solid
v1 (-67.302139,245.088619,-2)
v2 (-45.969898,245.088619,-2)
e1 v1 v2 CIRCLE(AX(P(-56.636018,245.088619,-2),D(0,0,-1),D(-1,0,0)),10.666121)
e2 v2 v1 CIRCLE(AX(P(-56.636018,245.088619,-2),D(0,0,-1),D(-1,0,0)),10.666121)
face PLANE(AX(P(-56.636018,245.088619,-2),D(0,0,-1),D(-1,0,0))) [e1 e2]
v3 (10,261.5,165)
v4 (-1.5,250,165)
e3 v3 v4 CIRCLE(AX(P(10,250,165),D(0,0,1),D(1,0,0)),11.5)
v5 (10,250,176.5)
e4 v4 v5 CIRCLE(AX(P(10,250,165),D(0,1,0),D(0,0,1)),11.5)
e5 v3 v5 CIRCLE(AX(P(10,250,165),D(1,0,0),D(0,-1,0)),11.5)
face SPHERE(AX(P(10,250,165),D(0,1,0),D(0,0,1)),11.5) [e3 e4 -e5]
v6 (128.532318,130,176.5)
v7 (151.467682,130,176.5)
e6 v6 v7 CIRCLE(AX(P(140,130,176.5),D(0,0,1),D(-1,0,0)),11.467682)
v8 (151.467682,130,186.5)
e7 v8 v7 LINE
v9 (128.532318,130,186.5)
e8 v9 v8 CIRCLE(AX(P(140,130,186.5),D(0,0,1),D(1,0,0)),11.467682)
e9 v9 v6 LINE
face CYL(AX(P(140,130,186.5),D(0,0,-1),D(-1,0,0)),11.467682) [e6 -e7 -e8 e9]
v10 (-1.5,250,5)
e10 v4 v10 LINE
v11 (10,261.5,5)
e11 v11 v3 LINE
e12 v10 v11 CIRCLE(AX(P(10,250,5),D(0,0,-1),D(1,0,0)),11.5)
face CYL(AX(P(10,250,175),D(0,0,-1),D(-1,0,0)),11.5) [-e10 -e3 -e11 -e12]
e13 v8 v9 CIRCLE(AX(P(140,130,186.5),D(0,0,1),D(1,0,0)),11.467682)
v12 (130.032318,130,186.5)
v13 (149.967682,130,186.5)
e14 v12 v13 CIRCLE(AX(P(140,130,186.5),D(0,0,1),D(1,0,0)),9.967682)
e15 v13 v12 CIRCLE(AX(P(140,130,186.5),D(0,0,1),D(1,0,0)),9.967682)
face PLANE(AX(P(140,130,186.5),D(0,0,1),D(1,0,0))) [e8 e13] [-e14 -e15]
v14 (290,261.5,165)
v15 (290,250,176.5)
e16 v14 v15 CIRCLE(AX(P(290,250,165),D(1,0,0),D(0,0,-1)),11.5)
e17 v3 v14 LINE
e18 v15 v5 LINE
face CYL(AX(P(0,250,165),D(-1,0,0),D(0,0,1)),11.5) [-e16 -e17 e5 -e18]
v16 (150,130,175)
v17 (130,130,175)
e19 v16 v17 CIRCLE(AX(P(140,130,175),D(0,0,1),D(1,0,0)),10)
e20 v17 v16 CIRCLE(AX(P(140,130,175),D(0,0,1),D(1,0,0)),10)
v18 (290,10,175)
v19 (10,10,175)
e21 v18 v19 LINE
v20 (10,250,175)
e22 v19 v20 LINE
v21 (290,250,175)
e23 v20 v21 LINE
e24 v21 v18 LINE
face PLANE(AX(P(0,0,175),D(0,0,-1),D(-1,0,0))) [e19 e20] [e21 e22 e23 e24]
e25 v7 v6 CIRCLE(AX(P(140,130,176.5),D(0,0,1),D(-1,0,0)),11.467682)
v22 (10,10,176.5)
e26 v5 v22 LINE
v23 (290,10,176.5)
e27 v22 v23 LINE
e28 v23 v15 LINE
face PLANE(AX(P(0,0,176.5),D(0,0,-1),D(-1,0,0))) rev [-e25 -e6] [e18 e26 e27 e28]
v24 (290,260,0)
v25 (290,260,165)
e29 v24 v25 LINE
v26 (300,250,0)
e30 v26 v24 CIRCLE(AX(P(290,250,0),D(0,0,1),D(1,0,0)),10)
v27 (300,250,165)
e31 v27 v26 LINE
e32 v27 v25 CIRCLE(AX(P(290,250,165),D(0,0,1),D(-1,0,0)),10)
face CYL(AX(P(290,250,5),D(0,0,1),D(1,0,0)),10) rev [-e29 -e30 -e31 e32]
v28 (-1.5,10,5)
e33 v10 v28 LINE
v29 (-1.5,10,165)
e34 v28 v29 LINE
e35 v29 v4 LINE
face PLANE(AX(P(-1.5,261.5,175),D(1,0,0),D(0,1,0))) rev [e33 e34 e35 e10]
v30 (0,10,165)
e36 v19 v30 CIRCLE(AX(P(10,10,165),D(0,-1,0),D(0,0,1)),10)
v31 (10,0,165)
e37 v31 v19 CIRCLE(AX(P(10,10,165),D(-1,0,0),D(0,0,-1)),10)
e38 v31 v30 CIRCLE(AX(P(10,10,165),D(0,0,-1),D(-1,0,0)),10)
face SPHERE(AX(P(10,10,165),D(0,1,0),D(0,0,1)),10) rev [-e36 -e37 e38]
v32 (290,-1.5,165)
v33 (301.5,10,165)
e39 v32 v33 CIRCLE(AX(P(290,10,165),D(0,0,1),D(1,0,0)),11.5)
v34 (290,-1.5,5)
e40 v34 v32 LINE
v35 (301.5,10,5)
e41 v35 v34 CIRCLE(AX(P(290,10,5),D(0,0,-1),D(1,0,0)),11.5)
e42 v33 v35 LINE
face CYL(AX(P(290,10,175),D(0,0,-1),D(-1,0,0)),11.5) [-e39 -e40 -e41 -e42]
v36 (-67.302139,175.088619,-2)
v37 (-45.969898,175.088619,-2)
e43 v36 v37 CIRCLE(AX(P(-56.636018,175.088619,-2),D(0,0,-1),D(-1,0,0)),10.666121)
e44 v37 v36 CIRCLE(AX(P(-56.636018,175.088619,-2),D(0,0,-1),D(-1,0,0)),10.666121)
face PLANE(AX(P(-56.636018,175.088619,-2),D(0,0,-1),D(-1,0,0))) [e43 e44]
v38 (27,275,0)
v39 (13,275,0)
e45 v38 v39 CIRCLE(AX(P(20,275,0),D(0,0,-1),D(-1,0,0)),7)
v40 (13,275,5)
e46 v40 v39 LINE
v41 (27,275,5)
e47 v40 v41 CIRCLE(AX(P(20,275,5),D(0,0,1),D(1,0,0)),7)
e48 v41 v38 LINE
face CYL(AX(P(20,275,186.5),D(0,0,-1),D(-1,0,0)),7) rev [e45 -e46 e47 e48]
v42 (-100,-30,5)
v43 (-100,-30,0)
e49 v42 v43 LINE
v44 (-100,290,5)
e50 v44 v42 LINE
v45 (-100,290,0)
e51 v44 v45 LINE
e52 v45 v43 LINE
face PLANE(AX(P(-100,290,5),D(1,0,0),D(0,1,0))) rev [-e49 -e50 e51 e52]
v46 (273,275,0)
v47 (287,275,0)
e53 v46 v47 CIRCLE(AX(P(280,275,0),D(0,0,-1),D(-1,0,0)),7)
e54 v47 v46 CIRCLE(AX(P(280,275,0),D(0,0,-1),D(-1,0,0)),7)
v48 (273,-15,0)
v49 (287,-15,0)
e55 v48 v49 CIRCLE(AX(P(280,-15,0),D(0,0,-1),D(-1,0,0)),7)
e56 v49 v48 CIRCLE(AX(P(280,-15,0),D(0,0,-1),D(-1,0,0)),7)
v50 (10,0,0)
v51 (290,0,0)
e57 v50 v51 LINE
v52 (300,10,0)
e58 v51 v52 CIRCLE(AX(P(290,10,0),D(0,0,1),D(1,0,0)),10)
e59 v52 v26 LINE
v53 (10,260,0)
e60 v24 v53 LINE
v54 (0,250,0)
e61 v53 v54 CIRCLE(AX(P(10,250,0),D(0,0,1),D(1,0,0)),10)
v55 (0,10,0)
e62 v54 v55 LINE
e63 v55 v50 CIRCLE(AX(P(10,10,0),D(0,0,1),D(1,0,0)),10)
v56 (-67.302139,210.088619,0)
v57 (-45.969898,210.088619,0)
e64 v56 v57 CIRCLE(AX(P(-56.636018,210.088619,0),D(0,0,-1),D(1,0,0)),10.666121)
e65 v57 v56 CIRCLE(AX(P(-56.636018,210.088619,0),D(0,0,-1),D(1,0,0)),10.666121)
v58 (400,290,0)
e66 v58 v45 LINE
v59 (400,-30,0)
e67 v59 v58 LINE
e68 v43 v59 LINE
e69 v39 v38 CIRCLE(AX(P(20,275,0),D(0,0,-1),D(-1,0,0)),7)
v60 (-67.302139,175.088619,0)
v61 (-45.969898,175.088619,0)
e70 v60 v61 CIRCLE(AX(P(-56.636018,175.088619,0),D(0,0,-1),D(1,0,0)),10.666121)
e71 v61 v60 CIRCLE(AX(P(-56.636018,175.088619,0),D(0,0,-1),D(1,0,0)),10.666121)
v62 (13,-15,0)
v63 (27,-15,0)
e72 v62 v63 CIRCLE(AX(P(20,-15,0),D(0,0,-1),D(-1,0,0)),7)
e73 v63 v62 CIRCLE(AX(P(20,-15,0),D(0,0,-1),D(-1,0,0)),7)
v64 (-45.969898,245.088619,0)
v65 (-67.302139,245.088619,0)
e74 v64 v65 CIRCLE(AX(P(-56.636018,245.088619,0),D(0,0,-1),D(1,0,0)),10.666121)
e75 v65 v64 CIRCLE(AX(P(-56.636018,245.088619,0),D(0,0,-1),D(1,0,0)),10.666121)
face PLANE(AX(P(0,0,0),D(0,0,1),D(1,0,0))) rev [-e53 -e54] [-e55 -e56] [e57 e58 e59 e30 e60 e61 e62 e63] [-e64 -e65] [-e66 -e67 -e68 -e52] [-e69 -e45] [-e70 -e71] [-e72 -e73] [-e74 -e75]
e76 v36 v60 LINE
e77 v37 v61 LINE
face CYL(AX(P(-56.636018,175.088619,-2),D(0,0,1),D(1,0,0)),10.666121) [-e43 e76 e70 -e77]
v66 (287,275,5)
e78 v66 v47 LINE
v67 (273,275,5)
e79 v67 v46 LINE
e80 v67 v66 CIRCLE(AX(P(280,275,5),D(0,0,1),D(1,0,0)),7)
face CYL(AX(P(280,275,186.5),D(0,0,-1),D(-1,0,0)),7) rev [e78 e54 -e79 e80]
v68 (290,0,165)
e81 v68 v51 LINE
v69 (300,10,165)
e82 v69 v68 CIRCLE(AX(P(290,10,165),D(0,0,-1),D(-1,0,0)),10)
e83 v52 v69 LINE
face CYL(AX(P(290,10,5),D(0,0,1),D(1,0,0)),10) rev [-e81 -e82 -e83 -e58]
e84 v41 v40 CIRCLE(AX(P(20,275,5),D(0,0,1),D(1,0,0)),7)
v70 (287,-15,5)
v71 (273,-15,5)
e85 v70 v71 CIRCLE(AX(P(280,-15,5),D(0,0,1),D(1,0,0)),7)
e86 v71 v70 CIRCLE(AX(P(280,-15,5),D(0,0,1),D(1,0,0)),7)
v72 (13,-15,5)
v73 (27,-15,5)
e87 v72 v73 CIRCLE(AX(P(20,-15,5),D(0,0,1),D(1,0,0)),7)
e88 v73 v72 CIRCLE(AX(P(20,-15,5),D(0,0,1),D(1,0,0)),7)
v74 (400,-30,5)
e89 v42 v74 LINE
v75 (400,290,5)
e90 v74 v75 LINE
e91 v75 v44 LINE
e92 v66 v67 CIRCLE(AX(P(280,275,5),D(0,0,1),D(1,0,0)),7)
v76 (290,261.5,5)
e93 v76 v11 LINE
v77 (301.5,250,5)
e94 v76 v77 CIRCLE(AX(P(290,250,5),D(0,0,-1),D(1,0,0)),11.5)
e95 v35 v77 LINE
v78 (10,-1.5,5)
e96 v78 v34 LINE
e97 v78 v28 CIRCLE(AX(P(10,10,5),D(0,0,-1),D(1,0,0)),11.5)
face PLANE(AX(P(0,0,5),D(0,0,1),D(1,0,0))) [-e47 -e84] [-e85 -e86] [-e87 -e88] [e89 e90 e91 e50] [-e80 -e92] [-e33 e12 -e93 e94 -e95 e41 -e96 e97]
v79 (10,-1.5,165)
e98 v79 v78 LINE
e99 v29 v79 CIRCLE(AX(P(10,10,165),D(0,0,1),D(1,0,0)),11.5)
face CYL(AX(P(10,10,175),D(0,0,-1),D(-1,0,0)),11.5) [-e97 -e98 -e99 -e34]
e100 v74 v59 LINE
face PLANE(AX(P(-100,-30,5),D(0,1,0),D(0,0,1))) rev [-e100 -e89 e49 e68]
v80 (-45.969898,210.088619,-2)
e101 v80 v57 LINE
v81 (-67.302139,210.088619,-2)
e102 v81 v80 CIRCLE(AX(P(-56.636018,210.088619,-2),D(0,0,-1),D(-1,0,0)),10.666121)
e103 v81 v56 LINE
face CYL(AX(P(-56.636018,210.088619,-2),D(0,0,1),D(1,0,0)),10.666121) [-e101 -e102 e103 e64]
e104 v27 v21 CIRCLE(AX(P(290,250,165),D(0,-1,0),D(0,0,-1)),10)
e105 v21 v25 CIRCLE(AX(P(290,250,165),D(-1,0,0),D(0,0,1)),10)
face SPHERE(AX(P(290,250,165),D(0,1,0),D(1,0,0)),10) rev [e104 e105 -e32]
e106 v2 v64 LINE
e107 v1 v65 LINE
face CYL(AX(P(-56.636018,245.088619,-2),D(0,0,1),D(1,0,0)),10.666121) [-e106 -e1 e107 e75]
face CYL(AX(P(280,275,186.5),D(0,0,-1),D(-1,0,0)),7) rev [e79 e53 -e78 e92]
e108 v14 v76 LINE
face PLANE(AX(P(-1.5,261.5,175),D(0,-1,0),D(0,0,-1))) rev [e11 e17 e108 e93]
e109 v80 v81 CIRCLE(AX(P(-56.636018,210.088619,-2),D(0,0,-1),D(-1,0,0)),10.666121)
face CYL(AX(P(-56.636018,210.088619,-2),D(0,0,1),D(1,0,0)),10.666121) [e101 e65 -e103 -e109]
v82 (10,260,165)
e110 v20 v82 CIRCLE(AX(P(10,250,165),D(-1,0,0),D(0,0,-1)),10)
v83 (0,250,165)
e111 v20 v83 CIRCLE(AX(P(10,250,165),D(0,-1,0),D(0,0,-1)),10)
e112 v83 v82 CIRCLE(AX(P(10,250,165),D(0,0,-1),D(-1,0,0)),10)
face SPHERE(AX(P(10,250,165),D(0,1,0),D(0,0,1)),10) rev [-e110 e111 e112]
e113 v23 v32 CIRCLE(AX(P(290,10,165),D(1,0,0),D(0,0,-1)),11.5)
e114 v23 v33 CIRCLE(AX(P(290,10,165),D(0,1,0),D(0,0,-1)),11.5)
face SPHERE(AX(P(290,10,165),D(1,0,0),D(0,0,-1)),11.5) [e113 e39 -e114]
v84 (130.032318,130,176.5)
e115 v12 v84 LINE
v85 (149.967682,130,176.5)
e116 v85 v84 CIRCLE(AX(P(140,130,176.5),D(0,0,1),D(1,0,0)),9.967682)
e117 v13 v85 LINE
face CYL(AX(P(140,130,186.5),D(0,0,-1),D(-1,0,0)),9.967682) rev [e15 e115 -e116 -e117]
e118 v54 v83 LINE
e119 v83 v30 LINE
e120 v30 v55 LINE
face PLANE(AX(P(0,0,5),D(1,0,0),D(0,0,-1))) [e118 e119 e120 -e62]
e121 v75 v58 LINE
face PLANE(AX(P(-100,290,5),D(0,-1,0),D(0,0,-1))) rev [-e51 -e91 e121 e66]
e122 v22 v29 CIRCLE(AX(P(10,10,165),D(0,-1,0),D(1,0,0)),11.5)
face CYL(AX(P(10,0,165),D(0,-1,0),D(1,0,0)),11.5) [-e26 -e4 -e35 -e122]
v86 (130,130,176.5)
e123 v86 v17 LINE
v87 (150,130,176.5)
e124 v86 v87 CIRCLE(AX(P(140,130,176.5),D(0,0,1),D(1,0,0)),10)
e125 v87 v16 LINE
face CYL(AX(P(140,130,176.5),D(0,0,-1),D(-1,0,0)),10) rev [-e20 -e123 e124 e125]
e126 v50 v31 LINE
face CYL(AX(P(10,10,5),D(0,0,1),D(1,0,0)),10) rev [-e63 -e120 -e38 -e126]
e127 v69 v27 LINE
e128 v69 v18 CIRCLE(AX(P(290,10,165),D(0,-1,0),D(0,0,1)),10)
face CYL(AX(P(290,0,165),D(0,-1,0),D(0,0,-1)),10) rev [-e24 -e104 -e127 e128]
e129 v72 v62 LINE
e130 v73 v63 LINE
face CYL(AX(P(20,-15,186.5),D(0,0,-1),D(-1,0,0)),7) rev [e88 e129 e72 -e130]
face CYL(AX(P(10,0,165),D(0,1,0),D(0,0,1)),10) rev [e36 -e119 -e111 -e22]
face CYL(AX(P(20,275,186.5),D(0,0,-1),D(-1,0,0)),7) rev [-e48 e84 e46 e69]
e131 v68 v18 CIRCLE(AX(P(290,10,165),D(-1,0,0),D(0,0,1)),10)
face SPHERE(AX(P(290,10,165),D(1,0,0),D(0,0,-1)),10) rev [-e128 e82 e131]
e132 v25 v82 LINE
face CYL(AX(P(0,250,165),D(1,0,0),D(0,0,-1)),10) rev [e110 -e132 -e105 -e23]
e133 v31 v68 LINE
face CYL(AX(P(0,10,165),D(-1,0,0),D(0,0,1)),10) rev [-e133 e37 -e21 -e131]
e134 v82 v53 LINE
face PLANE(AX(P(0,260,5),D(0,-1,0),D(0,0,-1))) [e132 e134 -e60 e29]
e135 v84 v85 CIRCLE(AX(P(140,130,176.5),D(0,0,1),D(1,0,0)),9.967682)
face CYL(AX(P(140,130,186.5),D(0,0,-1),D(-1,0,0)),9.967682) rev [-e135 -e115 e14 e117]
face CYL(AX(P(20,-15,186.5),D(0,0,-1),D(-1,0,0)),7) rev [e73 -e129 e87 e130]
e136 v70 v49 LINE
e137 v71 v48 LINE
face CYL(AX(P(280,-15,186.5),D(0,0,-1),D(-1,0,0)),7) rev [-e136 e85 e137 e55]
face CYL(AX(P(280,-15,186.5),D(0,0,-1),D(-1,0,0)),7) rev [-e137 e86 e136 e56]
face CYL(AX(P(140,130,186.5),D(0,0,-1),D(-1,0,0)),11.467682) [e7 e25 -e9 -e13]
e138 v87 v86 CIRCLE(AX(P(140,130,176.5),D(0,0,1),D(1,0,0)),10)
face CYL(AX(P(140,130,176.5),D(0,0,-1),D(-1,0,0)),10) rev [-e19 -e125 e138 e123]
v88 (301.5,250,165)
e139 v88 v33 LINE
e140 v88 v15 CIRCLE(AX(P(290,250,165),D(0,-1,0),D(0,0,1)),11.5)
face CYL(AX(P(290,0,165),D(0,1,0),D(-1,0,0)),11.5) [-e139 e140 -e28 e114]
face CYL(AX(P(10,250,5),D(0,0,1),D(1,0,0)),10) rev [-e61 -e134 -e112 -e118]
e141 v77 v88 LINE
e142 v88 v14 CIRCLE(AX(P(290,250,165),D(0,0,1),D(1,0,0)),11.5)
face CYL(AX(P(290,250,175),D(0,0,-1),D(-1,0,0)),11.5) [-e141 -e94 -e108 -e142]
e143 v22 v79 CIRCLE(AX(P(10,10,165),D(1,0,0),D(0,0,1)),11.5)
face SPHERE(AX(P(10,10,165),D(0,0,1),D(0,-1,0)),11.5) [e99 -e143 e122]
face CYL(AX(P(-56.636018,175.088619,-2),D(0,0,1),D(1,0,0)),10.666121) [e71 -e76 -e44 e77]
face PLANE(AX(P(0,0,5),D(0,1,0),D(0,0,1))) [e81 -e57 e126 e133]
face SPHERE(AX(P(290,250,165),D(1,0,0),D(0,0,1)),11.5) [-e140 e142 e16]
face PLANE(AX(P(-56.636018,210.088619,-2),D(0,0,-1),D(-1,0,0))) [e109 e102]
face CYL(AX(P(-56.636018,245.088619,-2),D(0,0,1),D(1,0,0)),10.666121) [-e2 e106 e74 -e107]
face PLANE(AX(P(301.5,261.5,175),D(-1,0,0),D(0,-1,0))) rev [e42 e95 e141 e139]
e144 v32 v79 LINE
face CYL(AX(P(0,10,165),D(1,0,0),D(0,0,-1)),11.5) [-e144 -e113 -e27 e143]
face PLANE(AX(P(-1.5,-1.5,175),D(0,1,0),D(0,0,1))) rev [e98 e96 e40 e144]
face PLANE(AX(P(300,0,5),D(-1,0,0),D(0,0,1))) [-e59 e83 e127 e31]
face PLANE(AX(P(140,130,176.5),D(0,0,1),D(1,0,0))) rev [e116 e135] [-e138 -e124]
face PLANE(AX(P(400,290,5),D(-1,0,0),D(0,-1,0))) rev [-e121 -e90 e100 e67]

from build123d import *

# Parameters (mm, degrees)
SKETCH1_W           = 500
SKETCH1_H           = 320
SKETCH1_W_2         = 300
SKETCH1_H_2         = 260
BOSS_EXTRUDE1_DEPTH = 5
SKETCH2_W           = 303
SKETCH2_H           = 263
SKETCH2_W_2         = 300
SKETCH2_H_2         = 260
BOSS_EXTRUDE2_DEPTH = 170
SKETCH3_W           = 303
SKETCH3_H           = 263
SKETCH3_R           = 10
BOSS_EXTRUDE3_DEPTH = 1.5
FILLET2_R           = 10
FILLET3_R           = 11.5
SKETCH4_R           = 11.467682252
SKETCH4_R_2         = 9.967682252
BOSS_EXTRUDE4_DEPTH = 10
SKETCH5_R           = 7
CUT_EXTRUDE1_DEPTH  = 529.093031577
SKETCH6_R           = 10.66612067
BOSS_EXTRUDE5_DEPTH = 2


with BuildPart() as part:
    # Sketch1 → Boss-Extrude1 (new body)
    with BuildSketch(Plane.XY):
        with Locations((150, 130)):
            Rectangle(SKETCH1_W, SKETCH1_H)
        with Locations((150, 130)):
            Rectangle(SKETCH1_W_2, SKETCH1_H_2, mode=Mode.SUBTRACT)
    extrude(amount=BOSS_EXTRUDE1_DEPTH)

    # Sketch2 → Boss-Extrude2 (add)
    with BuildSketch(Plane.XY.offset(5)):
        with Locations((150, 130)):
            Rectangle(SKETCH2_W, SKETCH2_H)
        with Locations((150, 130)):
            Rectangle(SKETCH2_W_2, SKETCH2_H_2, mode=Mode.SUBTRACT)
    extrude(amount=BOSS_EXTRUDE2_DEPTH)

    # Sketch3 → Boss-Extrude3 (add)
    with BuildSketch(Plane.XY.offset(175)):
        with Locations((150, 130)):
            Rectangle(SKETCH3_W, SKETCH3_H)
        with Locations((140, 130)):
            Circle(SKETCH3_R, mode=Mode.SUBTRACT)
    extrude(amount=BOSS_EXTRUDE3_DEPTH)

    # Fillet2
    fillet2_edges = [part.edges().sort_by_distance(p)[0] for p in [
        (0, 260, 87.5),
        (0, 0, 87.5),
        (300, 0, 87.5),
        (300, 260, 87.5),
        (0, 130, 175),
        (150, 0, 175),
        (300, 130, 175),
        (150, 260, 175),
    ]]
    fillet(fillet2_edges, radius=FILLET2_R)

    # Fillet3
    fillet3_edges = [part.edges().sort_by_distance(p)[0] for p in [
        (-1.5, 261.5, 90.75),
        (-1.5, -1.5, 90.75),
        (301.5, -1.5, 90.75),
        (301.5, 261.5, 90.75),
        (301.5, 130, 176.5),
        (150, 261.5, 176.5),
        (-1.5, 130, 176.5),
        (150, -1.5, 176.5),
    ]]
    fillet(fillet3_edges, radius=FILLET3_R)

    # Sketch4 → Boss-Extrude4 (add)
    with BuildSketch(Plane.XY.offset(176.5)):
        with Locations(Location((140, 130, 0), (0, 0, 180))):
            Circle(SKETCH4_R)
        with Locations((140, 130)):
            Circle(SKETCH4_R_2, mode=Mode.SUBTRACT)
    extrude(amount=BOSS_EXTRUDE4_DEPTH)

    # Sketch5 → Cut-Extrude1 (cut, through all)
    with BuildSketch(Plane(origin=(0, 0, 0), x_dir=(-1, 0, 0), z_dir=(0, 0, -1))):
        with Locations((-20, -15)):
            Circle(SKETCH5_R)
        with Locations((-280, -15)):
            Circle(SKETCH5_R)
        with Locations((-20, 275)):
            Circle(SKETCH5_R)
        with Locations((-280, 275)):
            Circle(SKETCH5_R)
    extrude(amount=-CUT_EXTRUDE1_DEPTH, mode=Mode.SUBTRACT)

    # Sketch6 → Boss-Extrude5 (add)
    with BuildSketch(Plane(origin=(0, 0, 0), x_dir=(-1, 0, 0), z_dir=(0, 0, -1))):
        with Locations(Location((56.636018442, 245.08861857, 0), (0, 0, 180))):
            Circle(SKETCH6_R)
        with Locations(Location((56.636018442, 210.08861857, 0), (0, 0, 180))):
            Circle(SKETCH6_R)
        with Locations(Location((56.636018442, 175.08861857, 0), (0, 0, 180))):
            Circle(SKETCH6_R)
    extrude(amount=BOSS_EXTRUDE5_DEPTH)


solid = part.part
